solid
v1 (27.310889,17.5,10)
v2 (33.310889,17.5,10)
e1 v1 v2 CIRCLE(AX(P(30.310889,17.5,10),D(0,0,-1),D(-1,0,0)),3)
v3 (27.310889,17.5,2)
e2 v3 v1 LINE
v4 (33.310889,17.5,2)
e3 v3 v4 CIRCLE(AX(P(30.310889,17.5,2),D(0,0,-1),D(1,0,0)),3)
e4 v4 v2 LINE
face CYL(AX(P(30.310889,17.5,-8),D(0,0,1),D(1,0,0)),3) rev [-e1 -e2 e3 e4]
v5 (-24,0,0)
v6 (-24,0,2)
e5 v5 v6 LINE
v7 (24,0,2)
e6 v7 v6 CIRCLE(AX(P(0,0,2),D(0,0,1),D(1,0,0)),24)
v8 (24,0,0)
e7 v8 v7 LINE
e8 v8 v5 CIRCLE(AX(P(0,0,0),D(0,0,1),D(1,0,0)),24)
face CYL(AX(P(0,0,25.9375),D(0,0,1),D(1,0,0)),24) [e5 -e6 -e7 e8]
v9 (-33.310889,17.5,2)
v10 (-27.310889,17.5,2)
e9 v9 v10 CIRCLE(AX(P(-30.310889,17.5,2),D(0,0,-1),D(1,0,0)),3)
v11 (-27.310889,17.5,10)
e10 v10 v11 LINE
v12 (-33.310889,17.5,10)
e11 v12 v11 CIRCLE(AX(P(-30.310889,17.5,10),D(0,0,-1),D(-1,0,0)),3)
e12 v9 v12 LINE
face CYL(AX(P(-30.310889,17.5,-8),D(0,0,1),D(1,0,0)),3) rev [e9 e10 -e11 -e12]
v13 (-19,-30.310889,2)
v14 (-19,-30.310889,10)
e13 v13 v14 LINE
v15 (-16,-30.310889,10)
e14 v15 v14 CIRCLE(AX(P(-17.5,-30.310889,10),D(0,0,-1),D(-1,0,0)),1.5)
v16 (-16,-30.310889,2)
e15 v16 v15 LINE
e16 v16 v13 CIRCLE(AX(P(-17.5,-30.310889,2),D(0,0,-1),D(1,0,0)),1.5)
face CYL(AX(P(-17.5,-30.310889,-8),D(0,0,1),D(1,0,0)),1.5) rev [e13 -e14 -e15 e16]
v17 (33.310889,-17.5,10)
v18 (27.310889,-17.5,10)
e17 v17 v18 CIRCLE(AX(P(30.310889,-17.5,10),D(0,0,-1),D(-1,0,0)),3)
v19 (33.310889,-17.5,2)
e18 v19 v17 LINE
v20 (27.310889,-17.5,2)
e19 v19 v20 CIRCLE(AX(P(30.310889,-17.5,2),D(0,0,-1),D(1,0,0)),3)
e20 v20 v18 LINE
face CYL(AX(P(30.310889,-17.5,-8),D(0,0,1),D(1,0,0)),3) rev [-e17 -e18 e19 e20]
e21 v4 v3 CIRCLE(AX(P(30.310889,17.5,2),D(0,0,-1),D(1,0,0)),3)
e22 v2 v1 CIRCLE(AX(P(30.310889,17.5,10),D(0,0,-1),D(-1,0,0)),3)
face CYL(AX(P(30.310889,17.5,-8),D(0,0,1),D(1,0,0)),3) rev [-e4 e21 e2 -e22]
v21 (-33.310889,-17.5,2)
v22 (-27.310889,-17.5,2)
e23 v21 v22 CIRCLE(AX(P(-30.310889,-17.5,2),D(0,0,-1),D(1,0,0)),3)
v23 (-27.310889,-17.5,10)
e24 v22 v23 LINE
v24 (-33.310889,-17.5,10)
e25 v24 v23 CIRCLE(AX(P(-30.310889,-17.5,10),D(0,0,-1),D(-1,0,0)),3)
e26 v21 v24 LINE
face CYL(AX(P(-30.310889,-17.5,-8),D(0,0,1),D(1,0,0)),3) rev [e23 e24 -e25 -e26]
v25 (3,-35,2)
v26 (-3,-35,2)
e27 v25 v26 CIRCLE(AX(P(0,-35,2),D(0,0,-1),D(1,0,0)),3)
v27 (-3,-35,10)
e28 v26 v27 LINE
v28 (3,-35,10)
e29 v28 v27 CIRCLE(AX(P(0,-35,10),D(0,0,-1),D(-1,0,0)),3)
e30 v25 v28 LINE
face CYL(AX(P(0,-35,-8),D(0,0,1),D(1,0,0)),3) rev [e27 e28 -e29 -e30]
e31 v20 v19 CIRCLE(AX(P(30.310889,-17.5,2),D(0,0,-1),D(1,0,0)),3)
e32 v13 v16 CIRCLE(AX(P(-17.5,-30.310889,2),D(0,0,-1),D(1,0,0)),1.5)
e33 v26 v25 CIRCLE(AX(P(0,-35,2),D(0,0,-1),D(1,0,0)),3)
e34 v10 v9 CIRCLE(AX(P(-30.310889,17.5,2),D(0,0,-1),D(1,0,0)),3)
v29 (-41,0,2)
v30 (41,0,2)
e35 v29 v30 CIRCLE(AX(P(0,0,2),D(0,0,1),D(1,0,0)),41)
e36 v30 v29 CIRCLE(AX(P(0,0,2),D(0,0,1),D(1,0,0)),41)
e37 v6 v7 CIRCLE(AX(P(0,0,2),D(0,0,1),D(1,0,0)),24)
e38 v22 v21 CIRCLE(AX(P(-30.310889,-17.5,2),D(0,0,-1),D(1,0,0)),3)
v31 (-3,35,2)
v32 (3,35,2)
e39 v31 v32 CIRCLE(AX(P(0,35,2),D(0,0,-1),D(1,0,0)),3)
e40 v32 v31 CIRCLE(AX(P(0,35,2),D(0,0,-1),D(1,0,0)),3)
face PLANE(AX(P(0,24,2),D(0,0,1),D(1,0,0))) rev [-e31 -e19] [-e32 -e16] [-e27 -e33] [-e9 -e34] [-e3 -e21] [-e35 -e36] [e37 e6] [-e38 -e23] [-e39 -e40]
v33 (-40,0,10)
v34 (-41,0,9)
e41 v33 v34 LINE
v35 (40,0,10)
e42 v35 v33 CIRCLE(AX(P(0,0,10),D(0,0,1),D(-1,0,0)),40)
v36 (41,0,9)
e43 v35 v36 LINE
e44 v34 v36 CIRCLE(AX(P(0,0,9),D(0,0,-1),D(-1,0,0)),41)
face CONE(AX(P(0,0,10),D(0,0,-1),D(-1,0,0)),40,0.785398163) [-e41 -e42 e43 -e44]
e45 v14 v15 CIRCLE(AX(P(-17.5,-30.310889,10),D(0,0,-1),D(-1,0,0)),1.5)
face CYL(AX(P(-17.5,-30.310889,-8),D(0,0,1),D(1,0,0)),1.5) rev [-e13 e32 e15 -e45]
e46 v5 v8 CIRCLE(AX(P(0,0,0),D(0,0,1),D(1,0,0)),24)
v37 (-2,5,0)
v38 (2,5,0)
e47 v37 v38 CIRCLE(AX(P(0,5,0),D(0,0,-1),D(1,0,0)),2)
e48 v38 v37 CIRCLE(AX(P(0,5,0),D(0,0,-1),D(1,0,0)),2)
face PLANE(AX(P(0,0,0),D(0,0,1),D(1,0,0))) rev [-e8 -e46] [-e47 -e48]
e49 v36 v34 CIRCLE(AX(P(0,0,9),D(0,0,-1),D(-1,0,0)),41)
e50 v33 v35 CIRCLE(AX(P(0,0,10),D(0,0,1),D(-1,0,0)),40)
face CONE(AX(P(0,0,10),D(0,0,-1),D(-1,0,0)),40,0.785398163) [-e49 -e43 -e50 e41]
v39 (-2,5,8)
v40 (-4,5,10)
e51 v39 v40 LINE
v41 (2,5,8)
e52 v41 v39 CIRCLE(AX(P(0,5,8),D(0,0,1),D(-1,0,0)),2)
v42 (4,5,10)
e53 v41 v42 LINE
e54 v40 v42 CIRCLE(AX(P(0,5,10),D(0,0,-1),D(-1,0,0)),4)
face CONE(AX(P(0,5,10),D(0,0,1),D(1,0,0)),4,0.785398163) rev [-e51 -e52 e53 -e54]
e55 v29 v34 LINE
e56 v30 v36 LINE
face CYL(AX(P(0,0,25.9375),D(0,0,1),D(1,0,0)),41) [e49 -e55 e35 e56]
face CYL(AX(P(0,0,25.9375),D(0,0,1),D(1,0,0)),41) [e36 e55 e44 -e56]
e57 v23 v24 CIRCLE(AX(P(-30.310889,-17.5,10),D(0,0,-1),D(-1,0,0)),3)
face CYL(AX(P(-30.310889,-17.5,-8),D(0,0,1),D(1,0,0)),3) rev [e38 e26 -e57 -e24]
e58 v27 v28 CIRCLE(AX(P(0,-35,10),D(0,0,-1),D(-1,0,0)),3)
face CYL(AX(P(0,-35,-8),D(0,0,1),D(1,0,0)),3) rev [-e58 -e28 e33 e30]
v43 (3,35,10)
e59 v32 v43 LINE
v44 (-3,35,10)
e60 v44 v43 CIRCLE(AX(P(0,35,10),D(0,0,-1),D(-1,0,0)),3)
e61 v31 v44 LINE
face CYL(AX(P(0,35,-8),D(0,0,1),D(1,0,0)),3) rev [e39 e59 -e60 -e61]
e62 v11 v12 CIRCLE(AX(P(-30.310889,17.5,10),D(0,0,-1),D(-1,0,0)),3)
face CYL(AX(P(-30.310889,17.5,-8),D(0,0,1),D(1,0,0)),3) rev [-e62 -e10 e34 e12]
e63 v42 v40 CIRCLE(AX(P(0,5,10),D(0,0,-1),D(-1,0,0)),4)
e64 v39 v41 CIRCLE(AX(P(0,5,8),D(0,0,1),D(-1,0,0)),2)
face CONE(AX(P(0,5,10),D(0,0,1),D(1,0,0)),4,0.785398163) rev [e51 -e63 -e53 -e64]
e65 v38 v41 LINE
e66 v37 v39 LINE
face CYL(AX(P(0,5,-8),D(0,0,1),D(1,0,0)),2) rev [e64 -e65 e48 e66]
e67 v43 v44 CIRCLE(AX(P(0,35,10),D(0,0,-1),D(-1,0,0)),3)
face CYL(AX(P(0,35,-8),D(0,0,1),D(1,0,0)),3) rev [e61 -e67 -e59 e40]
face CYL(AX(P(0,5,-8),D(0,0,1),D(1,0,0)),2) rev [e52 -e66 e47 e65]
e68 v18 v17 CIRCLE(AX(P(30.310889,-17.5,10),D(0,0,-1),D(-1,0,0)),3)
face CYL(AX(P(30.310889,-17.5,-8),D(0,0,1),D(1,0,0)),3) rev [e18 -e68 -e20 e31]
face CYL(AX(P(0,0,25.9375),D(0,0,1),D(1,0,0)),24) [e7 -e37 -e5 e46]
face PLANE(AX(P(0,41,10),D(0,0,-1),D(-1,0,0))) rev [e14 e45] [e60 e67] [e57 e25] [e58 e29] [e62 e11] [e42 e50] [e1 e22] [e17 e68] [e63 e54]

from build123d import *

# Parameters (mm, degrees)
CUT_EXTRUDE1_DEPTH      = 10
CUT_EXTRUDE1_DEPTH_BACK = 59.532042507
SKETCH2_R               = 3
SKETCH2_R_2             = 1.5
SKETCH2_R_3             = 2
CHAMFER1_SIZE           = 1
CHAMFER2_SIZE           = 2


with BuildPart() as part:
    # Sketch1 → Revolve1 (revolve)
    with BuildSketch(Plane(origin=(0, 0, 0), x_dir=(0, 0, -1), z_dir=(1, 0, 0)), mode=Mode.PRIVATE) as revolve1_sk:
        Polygon((0, 0), (0, 24), (-2, 24), (-2, 41), (-10, 41), (-10, 0), align=None)
    revolve(revolve1_sk.sketch.rotate(Axis((0, 0, 25.9375), (0, 0, -1)), 90), axis=Axis((0, 0, 25.9375), (0, 0, -1)))

    # Sketch2 → Cut-Extrude1 (cut, two sides: drawn at the far end of the back side and taken through both)
    with BuildSketch(Plane(origin=(0, 0, 2), x_dir=(-1, 0, 0), z_dir=(0, 0, -1)).offset(-CUT_EXTRUDE1_DEPTH_BACK)):
        with Locations(Location((0, 35, 0), (0, 0, 180))):
            Circle(SKETCH2_R)
        with Locations(Location((30.310889132, 17.5, 0), (0, 0, 180))):
            Circle(SKETCH2_R)
        with Locations(Location((30.310889132, -17.5, 0), (0, 0, 180))):
            Circle(SKETCH2_R)
        with Locations(Location((0, -35, 0), (0, 0, 180))):
            Circle(SKETCH2_R)
        with Locations(Location((-30.310889132, -17.5, 0), (0, 0, 180))):
            Circle(SKETCH2_R)
        with Locations(Location((-30.310889132, 17.5, 0), (0, 0, 180))):
            Circle(SKETCH2_R)
        with Locations(Location((17.5, -30.310889132, 0), (0, 0, 180))):
            Circle(SKETCH2_R_2)
        with Locations(Location((0, 5, 0), (0, 0, 180))):
            Circle(SKETCH2_R_3)
    extrude(amount=CUT_EXTRUDE1_DEPTH + CUT_EXTRUDE1_DEPTH_BACK, mode=Mode.SUBTRACT)

    # Chamfer1
    chamfer1_edges = [part.edges().sort_by_distance(p)[0] for p in [
        (-41, 0, 10),
    ]]
    chamfer(chamfer1_edges, length=CHAMFER1_SIZE)

    # Chamfer2
    chamfer2_edges = [part.edges().sort_by_distance(p)[0] for p in [
        (-2, 5, 10),
    ]]
    chamfer(chamfer2_edges, length=CHAMFER2_SIZE)


solid = part.part
